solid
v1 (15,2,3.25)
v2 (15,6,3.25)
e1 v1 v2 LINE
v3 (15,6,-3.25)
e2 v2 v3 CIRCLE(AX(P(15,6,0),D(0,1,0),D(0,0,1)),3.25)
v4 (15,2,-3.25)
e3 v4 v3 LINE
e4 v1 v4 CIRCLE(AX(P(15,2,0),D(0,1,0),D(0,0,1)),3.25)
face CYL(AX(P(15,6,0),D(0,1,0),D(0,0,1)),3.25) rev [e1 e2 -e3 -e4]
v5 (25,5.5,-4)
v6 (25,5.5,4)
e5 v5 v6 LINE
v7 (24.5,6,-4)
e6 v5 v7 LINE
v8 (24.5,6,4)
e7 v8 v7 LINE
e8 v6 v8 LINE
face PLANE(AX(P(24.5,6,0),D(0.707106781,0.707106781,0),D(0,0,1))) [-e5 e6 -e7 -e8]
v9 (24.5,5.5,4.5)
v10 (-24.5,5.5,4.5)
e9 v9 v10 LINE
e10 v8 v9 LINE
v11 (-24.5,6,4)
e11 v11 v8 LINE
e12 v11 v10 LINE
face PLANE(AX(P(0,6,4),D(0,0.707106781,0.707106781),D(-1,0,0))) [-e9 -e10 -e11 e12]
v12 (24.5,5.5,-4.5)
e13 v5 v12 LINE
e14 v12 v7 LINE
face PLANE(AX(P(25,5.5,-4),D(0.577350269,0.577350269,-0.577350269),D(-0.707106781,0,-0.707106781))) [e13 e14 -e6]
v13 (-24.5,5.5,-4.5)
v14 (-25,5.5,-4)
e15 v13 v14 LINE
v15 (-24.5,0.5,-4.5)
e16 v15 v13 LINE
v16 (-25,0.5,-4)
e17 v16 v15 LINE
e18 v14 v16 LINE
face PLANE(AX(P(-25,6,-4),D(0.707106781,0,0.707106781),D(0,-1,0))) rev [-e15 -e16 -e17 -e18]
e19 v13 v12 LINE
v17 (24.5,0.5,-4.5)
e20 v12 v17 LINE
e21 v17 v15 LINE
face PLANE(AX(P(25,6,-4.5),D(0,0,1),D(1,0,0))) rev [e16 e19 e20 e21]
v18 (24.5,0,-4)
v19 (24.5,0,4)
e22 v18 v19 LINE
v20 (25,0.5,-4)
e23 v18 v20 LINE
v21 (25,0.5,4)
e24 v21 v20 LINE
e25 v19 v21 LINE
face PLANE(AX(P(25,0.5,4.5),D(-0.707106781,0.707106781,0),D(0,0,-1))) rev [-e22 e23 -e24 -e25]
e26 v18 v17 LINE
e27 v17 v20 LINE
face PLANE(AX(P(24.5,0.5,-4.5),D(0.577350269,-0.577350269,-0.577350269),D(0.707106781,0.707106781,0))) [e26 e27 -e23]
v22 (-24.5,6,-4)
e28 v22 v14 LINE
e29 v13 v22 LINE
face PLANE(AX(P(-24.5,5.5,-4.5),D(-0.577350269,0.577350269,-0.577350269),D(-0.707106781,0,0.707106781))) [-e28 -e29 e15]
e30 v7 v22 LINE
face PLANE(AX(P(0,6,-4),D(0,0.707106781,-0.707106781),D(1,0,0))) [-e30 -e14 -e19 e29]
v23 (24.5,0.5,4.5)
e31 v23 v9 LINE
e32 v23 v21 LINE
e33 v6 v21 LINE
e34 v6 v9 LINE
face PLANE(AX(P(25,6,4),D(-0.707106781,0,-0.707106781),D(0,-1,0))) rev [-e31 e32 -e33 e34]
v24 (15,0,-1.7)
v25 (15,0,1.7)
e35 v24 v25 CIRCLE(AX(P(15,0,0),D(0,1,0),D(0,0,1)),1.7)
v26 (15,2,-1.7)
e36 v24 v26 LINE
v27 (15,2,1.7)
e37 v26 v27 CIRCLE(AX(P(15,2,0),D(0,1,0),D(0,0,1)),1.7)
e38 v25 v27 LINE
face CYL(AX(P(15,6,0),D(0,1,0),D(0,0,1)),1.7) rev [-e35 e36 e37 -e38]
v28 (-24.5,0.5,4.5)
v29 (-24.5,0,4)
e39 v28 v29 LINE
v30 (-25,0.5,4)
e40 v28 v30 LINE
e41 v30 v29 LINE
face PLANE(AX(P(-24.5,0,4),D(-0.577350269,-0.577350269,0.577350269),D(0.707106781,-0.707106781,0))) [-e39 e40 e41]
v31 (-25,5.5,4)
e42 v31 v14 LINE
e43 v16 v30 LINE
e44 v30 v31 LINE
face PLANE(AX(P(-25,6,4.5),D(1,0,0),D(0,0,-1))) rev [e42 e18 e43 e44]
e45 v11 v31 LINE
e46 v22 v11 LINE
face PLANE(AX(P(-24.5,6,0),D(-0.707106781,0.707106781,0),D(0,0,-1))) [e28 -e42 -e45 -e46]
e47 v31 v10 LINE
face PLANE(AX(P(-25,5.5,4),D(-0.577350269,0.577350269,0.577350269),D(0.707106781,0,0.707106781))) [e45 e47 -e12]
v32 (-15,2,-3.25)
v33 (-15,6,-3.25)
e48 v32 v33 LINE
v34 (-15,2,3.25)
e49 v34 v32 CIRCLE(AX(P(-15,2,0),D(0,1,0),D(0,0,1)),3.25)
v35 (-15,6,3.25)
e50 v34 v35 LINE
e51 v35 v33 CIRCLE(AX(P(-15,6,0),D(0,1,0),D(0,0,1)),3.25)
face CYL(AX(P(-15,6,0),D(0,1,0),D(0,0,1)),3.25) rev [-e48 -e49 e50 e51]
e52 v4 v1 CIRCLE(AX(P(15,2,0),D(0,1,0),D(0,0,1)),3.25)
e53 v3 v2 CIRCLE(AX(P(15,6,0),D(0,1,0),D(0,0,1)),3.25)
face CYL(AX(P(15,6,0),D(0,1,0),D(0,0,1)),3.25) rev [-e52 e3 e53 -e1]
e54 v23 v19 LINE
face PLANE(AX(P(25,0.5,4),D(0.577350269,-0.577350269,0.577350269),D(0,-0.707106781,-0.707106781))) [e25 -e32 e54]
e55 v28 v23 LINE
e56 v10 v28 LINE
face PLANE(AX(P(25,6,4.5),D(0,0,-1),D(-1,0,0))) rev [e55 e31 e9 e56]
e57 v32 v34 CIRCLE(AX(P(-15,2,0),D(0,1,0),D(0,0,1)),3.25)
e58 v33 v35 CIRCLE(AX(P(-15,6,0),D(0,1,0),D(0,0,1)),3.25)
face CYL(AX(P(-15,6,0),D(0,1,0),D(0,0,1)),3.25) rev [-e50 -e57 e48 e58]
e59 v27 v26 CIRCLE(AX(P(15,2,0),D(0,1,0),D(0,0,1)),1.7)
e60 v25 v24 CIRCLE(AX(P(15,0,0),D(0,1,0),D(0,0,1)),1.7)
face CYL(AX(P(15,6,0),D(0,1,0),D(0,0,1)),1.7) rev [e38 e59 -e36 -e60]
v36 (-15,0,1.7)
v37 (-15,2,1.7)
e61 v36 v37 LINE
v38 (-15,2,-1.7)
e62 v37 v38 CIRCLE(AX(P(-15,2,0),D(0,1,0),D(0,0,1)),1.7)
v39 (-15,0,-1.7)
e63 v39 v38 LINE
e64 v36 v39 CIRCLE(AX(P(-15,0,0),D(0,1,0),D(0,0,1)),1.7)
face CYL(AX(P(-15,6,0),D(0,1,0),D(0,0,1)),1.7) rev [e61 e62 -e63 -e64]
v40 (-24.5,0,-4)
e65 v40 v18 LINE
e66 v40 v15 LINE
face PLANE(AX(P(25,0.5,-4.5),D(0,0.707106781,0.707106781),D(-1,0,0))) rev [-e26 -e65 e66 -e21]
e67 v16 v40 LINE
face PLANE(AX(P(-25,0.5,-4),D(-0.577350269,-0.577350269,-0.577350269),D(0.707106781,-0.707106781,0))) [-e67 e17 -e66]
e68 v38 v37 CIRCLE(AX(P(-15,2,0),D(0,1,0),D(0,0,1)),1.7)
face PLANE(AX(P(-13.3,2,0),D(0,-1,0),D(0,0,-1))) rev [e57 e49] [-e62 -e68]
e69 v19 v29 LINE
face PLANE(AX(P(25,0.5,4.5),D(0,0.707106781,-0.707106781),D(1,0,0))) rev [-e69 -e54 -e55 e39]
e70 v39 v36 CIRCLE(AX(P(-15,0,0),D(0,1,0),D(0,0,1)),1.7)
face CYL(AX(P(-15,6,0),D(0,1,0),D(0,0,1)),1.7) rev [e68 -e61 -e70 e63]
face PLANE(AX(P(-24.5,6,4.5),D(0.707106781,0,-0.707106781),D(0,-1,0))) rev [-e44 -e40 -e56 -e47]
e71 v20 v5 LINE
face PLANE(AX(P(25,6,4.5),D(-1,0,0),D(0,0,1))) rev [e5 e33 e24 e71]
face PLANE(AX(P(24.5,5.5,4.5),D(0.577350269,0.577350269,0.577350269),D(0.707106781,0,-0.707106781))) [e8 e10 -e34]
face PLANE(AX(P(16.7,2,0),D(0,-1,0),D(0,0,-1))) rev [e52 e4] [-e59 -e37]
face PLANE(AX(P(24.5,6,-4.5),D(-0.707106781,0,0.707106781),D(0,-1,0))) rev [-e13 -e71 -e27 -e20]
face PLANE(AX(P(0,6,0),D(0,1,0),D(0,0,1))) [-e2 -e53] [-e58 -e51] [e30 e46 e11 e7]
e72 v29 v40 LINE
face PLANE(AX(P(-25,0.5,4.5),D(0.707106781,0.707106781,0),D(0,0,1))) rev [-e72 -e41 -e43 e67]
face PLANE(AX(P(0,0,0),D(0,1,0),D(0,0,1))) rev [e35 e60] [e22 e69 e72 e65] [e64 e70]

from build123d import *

# Parameters (mm, degrees)
SKETCH_1_W                   = 50
SKETCH_1_H                   = 9
EXTRUDE_1_DEPTH              = 6
CHAMFER_1_SIZE               = 0.5
HOLE_WIZARD_M3_1_D           = 3.4
HOLE_WIZARD_M3_1_CBORE_D     = 6.5
HOLE_WIZARD_M3_1_CBORE_DEPTH = 4


with BuildPart() as part:
    # 草图1 → 凸台-拉伸1 (new body)
    with BuildSketch(Plane(origin=(0, 0, 0), x_dir=(1, 0, 0), z_dir=(0, 1, 0))):
        Rectangle(SKETCH_1_W, SKETCH_1_H)
    extrude(amount=EXTRUDE_1_DEPTH)

    # 倒角1
    chamfer_1_edges = [part.edges().sort_by_distance(p)[0] for p in [
        (25, 6, 0),
        (0, 6, -4.5),
        (-25, 6, 0),
        (0, 0, -4.5),
        (25, 0, 0),
        (0, 0, 4.5),
        (-25, 0, 0),
        (-25, 3, -4.5),
        (25, 3, -4.5),
        (25, 3, 4.5),
        (-25, 3, 4.5),
        (0, 6, 4.5),
    ]]
    chamfer(chamfer_1_edges, length=CHAMFER_1_SIZE)

    # M3 六角凹头螺钉的柱形沉头孔1 (through all)
    with Locations(Plane(origin=(0, 6, 0), x_dir=(1, 0, 0), z_dir=(0, 1, 0))):
        with Locations((-15, 0), (15, 0)):
            CounterBoreHole(HOLE_WIZARD_M3_1_D / 2, HOLE_WIZARD_M3_1_CBORE_D / 2, HOLE_WIZARD_M3_1_CBORE_DEPTH)


solid = part.part
